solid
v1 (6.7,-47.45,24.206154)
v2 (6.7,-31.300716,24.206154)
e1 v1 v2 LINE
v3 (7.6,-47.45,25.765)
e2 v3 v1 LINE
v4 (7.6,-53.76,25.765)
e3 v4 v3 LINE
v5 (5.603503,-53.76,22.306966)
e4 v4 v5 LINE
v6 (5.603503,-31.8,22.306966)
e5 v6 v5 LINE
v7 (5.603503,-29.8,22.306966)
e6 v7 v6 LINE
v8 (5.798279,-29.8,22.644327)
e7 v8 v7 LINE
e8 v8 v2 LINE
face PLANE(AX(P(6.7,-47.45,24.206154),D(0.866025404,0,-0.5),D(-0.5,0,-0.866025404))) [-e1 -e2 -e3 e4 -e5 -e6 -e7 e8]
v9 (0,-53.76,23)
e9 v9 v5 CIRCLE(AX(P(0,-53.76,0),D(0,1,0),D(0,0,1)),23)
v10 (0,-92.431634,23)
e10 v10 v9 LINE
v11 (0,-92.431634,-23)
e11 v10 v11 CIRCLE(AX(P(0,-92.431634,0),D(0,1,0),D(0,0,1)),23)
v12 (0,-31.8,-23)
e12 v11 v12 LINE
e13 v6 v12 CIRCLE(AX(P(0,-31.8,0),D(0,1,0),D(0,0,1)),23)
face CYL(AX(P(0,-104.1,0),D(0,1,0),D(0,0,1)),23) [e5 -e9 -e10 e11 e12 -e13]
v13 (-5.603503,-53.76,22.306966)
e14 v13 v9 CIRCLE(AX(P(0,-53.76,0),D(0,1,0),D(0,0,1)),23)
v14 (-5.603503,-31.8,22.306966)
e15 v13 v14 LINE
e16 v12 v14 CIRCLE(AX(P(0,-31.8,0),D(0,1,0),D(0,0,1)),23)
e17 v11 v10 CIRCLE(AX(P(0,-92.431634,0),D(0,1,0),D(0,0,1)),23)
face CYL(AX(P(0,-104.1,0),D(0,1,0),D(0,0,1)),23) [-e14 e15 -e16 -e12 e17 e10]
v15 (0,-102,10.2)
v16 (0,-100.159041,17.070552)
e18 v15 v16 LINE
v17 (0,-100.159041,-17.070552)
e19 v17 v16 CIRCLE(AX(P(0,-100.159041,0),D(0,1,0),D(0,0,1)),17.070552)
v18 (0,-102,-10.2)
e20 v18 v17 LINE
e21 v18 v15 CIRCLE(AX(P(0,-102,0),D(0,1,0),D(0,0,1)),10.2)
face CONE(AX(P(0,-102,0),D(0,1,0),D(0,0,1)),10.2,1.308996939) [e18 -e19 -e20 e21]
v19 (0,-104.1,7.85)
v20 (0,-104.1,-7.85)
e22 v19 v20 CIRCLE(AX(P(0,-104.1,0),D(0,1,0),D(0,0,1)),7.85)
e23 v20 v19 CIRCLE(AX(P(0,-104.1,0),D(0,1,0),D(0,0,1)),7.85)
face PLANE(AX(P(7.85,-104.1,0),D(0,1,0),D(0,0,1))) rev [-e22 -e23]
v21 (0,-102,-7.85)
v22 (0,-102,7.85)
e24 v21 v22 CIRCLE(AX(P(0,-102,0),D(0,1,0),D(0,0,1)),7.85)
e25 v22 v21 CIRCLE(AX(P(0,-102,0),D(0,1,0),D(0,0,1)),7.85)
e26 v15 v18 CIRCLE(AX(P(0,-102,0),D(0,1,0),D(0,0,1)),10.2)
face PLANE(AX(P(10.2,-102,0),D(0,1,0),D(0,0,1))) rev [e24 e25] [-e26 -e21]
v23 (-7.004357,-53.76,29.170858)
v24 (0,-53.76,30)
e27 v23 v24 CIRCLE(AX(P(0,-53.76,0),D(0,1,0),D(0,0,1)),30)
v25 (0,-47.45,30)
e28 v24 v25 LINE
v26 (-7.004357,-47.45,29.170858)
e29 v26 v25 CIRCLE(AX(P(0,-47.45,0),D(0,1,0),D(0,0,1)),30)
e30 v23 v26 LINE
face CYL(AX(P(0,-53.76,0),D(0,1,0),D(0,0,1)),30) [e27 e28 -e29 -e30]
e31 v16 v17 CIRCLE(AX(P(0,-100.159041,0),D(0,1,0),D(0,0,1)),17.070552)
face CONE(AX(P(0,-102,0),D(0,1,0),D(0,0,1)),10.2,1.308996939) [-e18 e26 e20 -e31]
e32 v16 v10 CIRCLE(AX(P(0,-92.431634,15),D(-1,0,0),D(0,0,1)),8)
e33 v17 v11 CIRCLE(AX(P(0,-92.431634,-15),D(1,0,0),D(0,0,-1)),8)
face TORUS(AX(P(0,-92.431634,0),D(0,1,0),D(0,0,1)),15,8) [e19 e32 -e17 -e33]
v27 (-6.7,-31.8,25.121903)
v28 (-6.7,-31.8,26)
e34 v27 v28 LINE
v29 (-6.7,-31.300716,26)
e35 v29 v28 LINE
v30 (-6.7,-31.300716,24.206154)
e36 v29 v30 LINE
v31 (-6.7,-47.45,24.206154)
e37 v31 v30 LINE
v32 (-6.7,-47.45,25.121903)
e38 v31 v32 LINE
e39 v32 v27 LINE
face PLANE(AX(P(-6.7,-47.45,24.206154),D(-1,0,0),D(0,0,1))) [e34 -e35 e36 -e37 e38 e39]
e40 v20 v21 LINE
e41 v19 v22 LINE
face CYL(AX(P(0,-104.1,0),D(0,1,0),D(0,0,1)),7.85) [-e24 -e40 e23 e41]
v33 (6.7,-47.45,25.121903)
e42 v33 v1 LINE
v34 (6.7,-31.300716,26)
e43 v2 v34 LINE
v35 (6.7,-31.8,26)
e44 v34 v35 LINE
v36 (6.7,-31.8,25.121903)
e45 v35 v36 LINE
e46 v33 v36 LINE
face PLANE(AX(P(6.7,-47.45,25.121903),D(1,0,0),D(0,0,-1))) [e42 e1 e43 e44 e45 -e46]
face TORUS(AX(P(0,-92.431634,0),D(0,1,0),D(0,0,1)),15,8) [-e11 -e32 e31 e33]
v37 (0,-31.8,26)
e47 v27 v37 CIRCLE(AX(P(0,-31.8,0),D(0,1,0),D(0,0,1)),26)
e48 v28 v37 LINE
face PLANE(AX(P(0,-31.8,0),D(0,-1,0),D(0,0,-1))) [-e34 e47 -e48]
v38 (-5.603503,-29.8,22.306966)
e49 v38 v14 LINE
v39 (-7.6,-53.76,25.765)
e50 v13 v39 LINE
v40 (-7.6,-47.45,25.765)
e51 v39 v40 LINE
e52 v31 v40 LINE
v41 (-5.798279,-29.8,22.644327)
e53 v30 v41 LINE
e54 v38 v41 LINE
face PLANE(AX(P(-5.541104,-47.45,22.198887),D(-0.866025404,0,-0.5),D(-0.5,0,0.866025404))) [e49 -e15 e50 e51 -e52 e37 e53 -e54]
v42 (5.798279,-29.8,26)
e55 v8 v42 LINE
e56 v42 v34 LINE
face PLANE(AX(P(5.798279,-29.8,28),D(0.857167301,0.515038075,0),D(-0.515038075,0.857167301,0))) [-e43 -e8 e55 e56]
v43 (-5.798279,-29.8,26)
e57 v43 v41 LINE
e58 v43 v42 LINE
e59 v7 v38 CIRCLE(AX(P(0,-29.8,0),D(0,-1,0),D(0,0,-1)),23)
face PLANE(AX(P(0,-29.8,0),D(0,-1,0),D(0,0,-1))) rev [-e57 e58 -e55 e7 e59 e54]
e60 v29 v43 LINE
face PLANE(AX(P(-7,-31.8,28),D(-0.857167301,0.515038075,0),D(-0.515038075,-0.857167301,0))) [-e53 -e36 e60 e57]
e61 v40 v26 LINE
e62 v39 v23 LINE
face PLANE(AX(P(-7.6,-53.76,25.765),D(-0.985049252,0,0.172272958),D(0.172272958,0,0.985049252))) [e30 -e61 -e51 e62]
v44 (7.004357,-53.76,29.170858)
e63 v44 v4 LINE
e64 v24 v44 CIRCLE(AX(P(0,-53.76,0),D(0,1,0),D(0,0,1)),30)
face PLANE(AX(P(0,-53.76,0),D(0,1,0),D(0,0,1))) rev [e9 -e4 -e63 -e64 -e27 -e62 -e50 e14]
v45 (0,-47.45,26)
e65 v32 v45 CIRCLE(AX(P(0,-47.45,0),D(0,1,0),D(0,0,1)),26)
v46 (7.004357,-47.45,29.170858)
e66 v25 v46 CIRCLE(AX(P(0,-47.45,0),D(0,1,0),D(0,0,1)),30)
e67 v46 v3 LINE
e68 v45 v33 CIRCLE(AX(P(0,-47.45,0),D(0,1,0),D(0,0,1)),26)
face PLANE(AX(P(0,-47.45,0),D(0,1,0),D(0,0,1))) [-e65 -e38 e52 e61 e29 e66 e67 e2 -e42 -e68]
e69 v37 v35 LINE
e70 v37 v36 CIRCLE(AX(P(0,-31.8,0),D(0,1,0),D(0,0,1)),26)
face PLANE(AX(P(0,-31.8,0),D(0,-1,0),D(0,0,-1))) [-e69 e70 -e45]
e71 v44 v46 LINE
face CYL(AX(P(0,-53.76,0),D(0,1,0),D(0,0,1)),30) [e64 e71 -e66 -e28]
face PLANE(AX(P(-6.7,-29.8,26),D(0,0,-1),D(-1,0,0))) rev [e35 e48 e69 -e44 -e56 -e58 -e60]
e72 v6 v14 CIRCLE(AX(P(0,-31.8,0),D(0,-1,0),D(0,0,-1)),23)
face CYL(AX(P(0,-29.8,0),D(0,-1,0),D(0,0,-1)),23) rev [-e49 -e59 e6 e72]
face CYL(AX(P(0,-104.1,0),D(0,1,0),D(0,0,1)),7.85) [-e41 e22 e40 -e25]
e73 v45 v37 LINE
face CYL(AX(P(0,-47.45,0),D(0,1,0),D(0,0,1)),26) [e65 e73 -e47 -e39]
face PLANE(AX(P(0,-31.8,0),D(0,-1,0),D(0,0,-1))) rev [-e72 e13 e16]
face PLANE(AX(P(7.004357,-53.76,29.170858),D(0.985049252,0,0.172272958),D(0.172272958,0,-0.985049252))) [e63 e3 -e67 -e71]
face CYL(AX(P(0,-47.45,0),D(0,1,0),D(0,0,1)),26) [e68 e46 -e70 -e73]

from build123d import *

# Parameters (mm, degrees)
EXTRUDE_1_DEPTH     = 15.65
EXTRUDE_2_DEPTH     = 2
CUT_EXTRUDE_1_DEPTH = 28
EXTRUDE_3_DEPTH     = 6.31


with BuildPart() as part:
    # 草图1 → 旋转1 (revolve)
    with BuildSketch(Plane.XY, mode=Mode.PRIVATE) as revolve_1_sk:
        with BuildLine():
            Line((0, -31.8), (23, -31.8))
            Line((23, -31.8), (23, -92.431634433))
            ThreePointArc((23, -92.431634433), (21.346826722, -97.301725865), (17.070552361, -100.159041043))
            Line((17.070552361, -100.159041043), (10.2, -102))
            Line((10.2, -102), (7.85, -102))
            Line((7.85, -102), (7.85, -104.1))
            Line((7.85, -104.1), (0, -104.1))
            Line((0, -104.1), (0, -31.8))
        make_face()
    revolve(revolve_1_sk.sketch.rotate(Axis((0, -104.1, 0), (0, 1, 0)), 270), axis=Axis((0, -104.1, 0), (0, 1, 0)))

    # 草图2 → 凸台-拉伸1 (add)
    with BuildSketch(Plane(origin=(0, -31.8, 0), x_dir=(1, 0, 0), z_dir=(0, 1, 0))):
        with BuildLine():
            Line((6.7, -25.121902794), (6.7, -24.206154273))
            Line((6.7, -24.206154273), (5.541103538, -22.19888672))
            ThreePointArc((5.541103538, -22.19888672), (0, -22.88), (-5.541103538, -22.19888672))
            Line((-5.541103538, -22.19888672), (-6.7, -24.206154273))
            Line((-6.7, -24.206154273), (-6.7, -25.121902794))
            ThreePointArc((-6.7, -25.121902794), (0, -26), (6.7, -25.121902794))
        make_face()
    extrude(amount=-EXTRUDE_1_DEPTH)

    # 草图3 → 凸台-拉伸2 (add)
    with BuildSketch(Plane(origin=(0, -31.8, 0), x_dir=(1, 0, 0), z_dir=(0, 1, 0))):
        with BuildLine():
            Line((-6.7, -26), (6.7, -26))
            Line((6.7, -26), (6.7, -24.206154273))
            Line((6.7, -24.206154273), (5.60350337, -22.3069664))
            ThreePointArc((5.60350337, -22.3069664), (0, -23), (-5.60350337, -22.3069664))
            Line((-5.60350337, -22.3069664), (-6.7, -24.206154273))
            Line((-6.7, -24.206154273), (-6.7, -26))
        make_face()
    extrude(amount=EXTRUDE_2_DEPTH)

    # 草图4 → 切除-拉伸1 (cut)
    with BuildSketch(Plane.XY):
        Polygon((-7, -31.8), (-5.798278762, -29.8), (5.798278762, -29.8), (7, -31.8), (7, -27.8), (-7, -27.8), align=None)
    extrude(amount=CUT_EXTRUDE_1_DEPTH, mode=Mode.SUBTRACT)

    # 草图5 → 凸台-拉伸3 (add)
    with BuildSketch(Plane(origin=(0, -47.45, 0), x_dir=(1, 0, 0), z_dir=(0, 1, 0))):
        with BuildLine():
            Line((-7.6, -25.765), (-7.004357404, -29.170858358))
            ThreePointArc((-7.004357404, -29.170858358), (0, -30), (7.004357404, -29.170858358))
            Line((7.004357404, -29.170858358), (7.6, -25.765))
            Line((7.6, -25.765), (5.541103538, -22.19888672))
            ThreePointArc((5.541103538, -22.19888672), (0, -22.88), (-5.541103538, -22.19888672))
            Line((-5.541103538, -22.19888672), (-7.6, -25.765))
        make_face()
    extrude(amount=-EXTRUDE_3_DEPTH)


solid = part.part
